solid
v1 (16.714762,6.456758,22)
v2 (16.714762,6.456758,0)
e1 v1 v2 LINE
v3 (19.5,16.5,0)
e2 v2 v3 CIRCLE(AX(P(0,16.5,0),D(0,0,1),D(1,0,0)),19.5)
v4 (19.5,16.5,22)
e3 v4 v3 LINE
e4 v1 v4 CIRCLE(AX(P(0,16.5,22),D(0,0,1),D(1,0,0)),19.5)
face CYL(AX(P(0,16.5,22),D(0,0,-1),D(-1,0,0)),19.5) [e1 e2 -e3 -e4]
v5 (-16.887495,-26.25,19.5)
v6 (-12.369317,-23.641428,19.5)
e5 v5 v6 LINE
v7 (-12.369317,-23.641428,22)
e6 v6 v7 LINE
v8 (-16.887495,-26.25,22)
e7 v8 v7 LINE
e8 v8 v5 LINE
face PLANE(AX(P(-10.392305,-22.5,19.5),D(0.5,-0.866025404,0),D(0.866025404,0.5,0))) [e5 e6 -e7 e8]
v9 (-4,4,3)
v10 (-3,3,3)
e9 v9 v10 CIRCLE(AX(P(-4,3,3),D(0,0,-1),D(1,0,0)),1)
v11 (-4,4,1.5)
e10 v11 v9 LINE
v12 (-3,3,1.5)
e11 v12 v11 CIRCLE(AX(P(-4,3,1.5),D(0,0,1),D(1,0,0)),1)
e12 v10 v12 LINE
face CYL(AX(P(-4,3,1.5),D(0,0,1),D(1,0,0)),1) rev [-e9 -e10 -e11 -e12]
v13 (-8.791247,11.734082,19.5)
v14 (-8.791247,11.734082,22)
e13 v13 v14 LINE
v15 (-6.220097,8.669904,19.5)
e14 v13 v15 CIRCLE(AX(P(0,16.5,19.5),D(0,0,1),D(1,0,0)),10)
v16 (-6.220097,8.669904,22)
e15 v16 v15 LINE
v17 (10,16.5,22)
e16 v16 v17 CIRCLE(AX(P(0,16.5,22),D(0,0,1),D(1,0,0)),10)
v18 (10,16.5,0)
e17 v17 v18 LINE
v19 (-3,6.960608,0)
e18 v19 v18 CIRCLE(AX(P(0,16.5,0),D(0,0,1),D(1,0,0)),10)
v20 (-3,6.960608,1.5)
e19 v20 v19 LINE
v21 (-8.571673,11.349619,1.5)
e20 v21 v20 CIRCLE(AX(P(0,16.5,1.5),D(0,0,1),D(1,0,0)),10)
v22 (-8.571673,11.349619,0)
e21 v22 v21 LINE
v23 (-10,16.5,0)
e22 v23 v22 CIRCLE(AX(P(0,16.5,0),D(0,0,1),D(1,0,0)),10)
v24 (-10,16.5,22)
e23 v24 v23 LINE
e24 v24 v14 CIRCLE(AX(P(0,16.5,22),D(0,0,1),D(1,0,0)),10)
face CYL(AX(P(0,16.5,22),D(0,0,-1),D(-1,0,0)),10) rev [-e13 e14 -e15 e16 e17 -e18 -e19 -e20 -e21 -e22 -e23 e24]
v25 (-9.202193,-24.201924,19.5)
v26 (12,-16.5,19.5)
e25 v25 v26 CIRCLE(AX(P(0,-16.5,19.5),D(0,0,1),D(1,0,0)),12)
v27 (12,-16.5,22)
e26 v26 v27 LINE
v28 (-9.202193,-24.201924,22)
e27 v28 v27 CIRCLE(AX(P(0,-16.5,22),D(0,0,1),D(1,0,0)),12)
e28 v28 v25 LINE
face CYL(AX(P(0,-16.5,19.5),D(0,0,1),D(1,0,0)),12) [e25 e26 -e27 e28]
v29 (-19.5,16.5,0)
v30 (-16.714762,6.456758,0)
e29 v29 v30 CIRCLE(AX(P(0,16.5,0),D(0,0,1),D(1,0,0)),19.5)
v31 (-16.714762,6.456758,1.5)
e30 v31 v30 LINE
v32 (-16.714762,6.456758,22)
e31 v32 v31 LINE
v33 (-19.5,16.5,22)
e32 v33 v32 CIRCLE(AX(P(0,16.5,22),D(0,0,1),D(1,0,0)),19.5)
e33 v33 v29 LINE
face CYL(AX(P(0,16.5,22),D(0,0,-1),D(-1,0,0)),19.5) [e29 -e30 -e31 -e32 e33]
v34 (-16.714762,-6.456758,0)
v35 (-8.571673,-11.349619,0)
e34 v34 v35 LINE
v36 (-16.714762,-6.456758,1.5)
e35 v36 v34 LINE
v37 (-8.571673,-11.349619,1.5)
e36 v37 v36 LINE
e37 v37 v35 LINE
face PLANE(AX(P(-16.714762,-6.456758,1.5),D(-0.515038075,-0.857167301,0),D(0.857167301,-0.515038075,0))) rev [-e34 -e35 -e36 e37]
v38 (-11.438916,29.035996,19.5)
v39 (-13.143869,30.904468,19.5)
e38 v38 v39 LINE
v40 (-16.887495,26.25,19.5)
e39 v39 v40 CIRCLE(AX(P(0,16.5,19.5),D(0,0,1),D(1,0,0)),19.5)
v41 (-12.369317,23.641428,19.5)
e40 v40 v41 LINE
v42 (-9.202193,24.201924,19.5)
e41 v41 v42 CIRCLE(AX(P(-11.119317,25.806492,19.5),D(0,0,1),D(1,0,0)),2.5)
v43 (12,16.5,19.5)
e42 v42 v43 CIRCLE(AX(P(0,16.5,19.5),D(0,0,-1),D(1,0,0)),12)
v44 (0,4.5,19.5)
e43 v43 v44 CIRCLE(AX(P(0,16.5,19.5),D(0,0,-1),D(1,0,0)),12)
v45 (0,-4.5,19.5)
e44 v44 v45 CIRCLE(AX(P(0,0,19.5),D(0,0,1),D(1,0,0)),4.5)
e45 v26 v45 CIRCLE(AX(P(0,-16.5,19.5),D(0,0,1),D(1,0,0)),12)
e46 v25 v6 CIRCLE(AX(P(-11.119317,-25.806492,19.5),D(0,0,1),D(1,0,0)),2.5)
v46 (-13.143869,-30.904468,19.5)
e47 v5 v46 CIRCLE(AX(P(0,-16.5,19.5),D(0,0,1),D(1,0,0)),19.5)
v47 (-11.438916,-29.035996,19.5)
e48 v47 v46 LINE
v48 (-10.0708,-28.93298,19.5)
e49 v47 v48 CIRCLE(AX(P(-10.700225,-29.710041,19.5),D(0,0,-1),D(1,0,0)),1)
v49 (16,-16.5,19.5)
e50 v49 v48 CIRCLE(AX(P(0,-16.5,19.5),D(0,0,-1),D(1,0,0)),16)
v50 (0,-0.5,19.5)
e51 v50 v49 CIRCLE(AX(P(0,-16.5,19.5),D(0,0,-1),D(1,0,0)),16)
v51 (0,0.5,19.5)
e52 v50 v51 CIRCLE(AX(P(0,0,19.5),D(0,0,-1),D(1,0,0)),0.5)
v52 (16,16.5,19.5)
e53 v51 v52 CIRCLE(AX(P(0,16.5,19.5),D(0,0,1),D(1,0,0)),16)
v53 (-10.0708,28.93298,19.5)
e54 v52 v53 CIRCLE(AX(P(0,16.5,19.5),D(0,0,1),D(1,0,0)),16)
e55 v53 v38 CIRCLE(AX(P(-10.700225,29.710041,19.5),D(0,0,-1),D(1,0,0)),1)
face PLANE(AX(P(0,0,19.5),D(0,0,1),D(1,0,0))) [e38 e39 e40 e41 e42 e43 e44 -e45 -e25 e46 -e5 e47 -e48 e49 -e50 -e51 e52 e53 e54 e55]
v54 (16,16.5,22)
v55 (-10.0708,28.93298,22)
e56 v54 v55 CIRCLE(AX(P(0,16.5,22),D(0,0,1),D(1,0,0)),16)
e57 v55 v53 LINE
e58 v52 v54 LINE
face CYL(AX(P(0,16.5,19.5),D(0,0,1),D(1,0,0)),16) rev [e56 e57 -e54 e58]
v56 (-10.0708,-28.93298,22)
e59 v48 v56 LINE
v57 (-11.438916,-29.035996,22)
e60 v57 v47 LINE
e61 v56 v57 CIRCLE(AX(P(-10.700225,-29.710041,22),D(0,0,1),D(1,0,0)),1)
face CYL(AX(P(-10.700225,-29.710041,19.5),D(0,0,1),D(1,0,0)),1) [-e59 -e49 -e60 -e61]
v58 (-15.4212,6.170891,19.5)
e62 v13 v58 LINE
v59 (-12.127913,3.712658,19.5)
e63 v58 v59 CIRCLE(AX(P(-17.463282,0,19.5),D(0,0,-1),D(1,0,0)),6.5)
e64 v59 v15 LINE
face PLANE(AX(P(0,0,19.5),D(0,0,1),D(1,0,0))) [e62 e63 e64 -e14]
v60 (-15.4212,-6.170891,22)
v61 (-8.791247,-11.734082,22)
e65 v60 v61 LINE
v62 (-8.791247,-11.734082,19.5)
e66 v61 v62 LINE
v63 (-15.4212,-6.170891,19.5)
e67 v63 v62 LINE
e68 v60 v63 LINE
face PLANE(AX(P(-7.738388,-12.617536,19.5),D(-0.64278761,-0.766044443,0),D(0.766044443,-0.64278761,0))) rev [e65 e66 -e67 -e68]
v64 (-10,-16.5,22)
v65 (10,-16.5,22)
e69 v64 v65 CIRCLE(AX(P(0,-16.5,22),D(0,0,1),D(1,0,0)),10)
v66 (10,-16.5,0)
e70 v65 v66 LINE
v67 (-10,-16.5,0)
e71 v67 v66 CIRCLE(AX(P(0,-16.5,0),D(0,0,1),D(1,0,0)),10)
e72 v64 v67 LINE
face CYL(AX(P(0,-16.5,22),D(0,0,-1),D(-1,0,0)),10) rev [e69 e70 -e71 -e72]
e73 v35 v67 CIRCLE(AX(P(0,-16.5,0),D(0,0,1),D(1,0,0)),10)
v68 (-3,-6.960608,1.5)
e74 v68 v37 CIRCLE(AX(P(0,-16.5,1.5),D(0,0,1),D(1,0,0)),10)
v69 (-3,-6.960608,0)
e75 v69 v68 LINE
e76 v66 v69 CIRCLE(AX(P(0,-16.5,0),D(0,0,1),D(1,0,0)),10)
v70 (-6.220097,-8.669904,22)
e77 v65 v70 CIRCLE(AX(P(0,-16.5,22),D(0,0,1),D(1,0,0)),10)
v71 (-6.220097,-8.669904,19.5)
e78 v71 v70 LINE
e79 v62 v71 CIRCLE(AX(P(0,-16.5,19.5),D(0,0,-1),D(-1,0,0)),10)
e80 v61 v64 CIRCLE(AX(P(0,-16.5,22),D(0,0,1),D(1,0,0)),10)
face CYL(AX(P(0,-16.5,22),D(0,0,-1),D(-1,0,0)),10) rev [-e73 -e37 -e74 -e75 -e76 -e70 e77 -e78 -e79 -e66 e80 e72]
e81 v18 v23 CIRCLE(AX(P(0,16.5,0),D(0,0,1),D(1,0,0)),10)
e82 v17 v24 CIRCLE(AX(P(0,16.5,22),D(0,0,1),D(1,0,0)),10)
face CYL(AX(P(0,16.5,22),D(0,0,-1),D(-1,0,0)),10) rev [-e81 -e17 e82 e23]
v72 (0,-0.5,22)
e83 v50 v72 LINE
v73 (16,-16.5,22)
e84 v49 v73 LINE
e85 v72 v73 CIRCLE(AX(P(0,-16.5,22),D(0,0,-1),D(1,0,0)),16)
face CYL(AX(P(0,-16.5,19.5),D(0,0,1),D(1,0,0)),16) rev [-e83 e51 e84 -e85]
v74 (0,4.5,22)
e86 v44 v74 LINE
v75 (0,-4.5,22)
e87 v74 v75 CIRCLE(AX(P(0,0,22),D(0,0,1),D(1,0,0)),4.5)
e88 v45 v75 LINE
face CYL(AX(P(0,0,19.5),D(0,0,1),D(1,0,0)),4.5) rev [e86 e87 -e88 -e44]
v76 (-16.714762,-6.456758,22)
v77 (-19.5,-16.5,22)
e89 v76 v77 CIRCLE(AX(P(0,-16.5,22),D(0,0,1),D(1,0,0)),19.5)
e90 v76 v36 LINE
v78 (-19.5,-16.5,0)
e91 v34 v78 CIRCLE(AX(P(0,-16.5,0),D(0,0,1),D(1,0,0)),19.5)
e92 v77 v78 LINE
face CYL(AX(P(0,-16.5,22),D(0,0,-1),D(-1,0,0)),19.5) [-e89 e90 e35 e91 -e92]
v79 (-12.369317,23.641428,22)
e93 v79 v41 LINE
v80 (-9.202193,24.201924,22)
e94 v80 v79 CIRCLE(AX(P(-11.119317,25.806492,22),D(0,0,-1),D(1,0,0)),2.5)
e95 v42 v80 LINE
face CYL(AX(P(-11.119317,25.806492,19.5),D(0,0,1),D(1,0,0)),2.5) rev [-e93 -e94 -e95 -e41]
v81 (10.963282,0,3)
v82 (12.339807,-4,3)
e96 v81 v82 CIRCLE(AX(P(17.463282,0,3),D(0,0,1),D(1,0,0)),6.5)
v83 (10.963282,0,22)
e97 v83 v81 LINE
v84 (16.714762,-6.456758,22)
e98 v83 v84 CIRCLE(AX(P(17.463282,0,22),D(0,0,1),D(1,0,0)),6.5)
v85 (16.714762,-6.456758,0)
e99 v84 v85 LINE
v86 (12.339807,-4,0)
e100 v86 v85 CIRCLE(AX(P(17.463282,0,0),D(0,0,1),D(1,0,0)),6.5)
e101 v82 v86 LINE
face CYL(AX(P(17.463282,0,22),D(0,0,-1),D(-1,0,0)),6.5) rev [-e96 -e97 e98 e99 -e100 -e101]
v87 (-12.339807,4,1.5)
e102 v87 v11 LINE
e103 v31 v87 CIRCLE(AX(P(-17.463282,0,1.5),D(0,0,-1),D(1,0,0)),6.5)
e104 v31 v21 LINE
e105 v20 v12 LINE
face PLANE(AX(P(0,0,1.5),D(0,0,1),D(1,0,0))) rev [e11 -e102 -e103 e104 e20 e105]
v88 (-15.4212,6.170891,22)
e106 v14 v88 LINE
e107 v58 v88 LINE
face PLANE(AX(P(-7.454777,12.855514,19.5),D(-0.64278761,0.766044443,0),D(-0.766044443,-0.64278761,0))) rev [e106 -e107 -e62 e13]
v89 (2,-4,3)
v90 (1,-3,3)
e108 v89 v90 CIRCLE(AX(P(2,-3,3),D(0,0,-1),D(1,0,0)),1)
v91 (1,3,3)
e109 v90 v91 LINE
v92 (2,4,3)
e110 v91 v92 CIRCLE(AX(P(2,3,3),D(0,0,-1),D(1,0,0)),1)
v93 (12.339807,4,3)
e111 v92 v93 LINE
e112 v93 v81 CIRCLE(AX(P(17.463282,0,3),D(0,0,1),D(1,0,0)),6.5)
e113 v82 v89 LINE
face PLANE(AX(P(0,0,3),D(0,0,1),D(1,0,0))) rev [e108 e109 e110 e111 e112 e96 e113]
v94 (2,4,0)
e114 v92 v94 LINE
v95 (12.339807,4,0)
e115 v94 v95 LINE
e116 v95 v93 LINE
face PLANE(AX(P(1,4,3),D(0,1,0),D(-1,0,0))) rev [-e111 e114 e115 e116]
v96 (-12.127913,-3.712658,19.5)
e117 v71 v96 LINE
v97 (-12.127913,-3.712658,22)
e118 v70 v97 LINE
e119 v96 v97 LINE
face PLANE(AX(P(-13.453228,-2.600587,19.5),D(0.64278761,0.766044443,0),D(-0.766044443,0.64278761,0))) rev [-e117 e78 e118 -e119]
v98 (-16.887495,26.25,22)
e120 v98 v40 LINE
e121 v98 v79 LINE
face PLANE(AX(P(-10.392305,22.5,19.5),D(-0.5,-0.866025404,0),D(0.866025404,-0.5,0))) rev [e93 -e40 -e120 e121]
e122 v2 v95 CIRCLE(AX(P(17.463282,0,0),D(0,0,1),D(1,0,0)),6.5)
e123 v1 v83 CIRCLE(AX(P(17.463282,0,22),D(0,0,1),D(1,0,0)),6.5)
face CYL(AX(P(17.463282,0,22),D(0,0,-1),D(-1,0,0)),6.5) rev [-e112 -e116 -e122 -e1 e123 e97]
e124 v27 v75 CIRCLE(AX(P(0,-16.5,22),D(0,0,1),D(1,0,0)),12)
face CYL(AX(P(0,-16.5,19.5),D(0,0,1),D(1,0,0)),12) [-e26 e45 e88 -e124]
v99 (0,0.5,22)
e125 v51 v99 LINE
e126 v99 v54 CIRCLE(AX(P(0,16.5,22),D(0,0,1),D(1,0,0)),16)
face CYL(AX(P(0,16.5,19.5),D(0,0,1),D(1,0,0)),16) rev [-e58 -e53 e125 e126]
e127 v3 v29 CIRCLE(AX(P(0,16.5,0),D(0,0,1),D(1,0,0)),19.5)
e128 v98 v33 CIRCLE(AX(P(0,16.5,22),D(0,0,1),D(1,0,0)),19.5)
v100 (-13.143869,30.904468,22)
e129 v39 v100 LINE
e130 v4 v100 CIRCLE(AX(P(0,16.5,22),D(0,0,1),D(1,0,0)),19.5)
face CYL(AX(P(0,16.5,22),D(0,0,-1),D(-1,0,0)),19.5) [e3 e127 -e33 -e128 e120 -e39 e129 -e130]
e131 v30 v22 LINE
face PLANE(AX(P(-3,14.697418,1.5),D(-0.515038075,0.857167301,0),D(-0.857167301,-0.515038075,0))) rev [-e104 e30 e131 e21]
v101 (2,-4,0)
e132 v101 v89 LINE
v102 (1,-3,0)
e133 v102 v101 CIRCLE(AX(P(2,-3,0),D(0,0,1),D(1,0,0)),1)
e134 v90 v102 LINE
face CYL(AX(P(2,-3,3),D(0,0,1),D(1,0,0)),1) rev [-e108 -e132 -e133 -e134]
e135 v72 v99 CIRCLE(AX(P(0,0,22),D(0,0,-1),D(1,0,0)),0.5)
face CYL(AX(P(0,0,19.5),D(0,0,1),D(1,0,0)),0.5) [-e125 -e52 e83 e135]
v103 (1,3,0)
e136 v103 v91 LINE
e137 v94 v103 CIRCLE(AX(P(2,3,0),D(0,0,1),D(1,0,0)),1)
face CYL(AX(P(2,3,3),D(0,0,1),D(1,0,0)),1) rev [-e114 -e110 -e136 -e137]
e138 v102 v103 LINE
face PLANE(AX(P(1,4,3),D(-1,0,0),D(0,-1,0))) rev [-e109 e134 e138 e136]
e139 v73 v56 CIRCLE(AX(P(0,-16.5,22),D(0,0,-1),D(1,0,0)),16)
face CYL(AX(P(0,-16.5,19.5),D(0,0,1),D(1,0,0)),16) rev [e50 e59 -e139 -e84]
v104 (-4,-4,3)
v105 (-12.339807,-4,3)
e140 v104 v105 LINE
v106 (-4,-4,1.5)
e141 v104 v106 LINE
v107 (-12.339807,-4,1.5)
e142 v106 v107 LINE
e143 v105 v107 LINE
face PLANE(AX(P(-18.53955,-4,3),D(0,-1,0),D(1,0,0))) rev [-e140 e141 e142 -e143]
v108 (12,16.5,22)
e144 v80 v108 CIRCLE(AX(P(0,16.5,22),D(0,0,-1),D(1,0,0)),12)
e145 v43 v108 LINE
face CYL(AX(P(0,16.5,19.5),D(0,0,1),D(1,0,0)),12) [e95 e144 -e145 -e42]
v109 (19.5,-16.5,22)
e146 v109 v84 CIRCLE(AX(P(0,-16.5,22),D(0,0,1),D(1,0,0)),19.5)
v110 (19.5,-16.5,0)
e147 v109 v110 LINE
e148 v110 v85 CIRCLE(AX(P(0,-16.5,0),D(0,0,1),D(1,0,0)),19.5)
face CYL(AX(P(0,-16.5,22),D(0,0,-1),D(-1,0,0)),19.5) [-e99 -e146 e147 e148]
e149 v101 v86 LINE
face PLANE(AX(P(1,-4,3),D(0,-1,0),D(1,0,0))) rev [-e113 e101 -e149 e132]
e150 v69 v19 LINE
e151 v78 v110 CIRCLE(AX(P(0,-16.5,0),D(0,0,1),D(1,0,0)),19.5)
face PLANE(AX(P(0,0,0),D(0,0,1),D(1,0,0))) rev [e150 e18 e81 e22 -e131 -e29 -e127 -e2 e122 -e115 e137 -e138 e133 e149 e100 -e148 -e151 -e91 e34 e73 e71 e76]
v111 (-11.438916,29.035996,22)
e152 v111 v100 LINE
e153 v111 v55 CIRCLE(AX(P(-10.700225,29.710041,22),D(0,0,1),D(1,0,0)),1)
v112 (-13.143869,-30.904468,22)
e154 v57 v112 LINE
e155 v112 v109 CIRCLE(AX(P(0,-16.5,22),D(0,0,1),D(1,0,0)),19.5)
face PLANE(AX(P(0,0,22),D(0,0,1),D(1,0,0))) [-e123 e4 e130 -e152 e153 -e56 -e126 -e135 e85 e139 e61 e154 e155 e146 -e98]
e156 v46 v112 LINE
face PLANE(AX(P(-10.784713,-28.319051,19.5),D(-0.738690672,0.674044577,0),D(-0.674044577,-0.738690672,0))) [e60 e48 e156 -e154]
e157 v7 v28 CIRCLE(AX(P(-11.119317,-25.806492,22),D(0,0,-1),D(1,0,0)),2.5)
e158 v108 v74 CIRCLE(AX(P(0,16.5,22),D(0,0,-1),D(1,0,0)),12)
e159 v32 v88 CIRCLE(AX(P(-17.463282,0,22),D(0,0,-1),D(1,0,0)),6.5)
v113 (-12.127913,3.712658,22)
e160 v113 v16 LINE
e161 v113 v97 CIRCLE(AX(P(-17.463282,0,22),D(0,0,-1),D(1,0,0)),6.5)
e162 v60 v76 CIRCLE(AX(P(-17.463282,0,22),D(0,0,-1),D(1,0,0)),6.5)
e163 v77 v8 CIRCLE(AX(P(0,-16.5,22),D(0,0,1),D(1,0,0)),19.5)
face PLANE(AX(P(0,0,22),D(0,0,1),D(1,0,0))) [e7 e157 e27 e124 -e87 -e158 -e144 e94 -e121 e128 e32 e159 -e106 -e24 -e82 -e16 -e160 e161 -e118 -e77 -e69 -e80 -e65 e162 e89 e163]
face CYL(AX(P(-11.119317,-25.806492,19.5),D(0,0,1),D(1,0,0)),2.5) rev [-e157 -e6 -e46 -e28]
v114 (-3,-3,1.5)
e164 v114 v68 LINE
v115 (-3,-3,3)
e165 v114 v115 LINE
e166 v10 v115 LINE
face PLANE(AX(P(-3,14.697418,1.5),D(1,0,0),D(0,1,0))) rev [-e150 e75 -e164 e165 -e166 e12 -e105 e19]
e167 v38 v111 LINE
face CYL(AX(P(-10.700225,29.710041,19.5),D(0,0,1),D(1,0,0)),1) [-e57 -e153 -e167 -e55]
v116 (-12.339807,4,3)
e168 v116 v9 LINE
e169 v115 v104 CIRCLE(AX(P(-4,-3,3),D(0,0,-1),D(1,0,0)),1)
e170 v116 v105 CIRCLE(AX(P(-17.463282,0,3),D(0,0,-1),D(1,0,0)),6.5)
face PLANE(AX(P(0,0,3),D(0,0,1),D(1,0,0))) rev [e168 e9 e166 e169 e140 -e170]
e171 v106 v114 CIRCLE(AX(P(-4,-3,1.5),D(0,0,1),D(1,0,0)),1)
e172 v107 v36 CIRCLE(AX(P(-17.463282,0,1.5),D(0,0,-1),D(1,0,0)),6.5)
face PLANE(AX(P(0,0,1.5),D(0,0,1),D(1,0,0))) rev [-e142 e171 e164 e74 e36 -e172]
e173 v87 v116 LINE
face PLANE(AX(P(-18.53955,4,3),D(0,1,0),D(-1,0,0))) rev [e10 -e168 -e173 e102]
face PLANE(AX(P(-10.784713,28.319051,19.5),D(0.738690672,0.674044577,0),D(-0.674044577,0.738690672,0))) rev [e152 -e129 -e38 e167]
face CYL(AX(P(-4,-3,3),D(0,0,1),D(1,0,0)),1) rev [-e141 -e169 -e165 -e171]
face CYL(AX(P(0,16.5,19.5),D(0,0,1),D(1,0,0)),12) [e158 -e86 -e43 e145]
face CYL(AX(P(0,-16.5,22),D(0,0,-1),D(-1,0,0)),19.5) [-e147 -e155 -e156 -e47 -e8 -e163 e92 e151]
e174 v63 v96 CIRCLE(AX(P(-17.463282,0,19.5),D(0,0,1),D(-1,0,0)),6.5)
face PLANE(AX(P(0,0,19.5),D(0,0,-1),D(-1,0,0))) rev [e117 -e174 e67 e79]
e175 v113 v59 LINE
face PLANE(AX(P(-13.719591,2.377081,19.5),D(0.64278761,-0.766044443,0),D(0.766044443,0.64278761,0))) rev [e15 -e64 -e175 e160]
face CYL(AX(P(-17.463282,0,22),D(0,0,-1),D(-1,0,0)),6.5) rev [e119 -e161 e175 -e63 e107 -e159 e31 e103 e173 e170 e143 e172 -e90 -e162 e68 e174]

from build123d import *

# Parameters (mm, degrees)
SKETCH_1_R             = 10
EXTRUDE_1_DEPTH        = 22
CUT_EXTRUDE_1_DEPTH    = 2.5
FILLET_1_R             = 1
FILLET_2_R             = 2.5
FILLET_1_OF_MIRROR_1_R = 1
FILLET_2_OF_MIRROR_1_R = 2.5
CUT_EXTRUDE_2_DEPTH    = 2.5
CUT_EXTRUDE_3_DEPTH    = 1.5
SKETCH_5_W             = 15.539550215
SKETCH_5_H             = 8
CUT_EXTRUDE_4_DEPTH    = 1.5
SKETCH_6_W             = 13.998675607
SKETCH_6_H             = 8
CUT_EXTRUDE_5_DEPTH    = 3
FILLET_3_R             = 1


with BuildPart() as part:
    # 草图1 → 凸台-拉伸1 (new body)
    with BuildSketch(Plane.XY):
        with BuildLine():
            ThreePointArc((16.714762364, 6.456757539), (0, 36), (-16.714762364, 6.456757539))
            ThreePointArc((-16.714762364, 6.456757539), (-10.963282289, 0), (-16.714762364, -6.456757539))
            ThreePointArc((-16.714762364, -6.456757539), (0, -36), (16.714762364, -6.456757539))
            ThreePointArc((16.714762364, -6.456757539), (10.963282289, 0), (16.714762364, 6.456757539))
        make_face()
        with Locations((0, 16.5)):
            Circle(SKETCH_1_R, mode=Mode.SUBTRACT)
        with Locations((0, -16.5)):
            Circle(SKETCH_1_R, mode=Mode.SUBTRACT)
    extrude(amount=EXTRUDE_1_DEPTH)

    # 草图2 → 切除-拉伸1 (cut)
    with BuildSketch(Plane.XY.offset(22)):
        with BuildLine():
            Line((-10.392304845, 22.5), (-20.279992845, 28.208659328))
            Line((-20.279992845, 28.208659328), (-16.120486586, 34.166566083))
            Line((-16.120486586, 34.166566083), (-10.784713231, 28.319050745))
            ThreePointArc((-10.784713231, 28.319050745), (14.918190439, 22.283389494), (0, 0.5))
            ThreePointArc((0, 0.5), (-0.353553391, 0.353553391), (-0.5, 0))
            Line((-0.5, 0), (-4.5, 0))
            ThreePointArc((-4.5, 0), (-3.181980515, 3.181980515), (0, 4.5))
            ThreePointArc((0, 4.5), (10.392304845, 22.5), (-10.392304845, 22.5))
        make_face()
    cut_extrude_1 = extrude(amount=-CUT_EXTRUDE_1_DEPTH, mode=Mode.SUBTRACT)

    # 圆角1
    fillet_1_edges = [part.edges().sort_by_distance(p)[0] for p in [
        (-10.784713231, 28.319050745, 20.75),
    ]]
    fillet(fillet_1_edges, radius=FILLET_1_R)

    # 圆角2
    fillet_2_edges = [part.edges().sort_by_distance(p)[0] for p in [
        (-10.392304845, 22.5, 20.75),
    ]]
    fillet(fillet_2_edges, radius=FILLET_2_R)

    # 镜向1: 切除-拉伸1 across plane
    add(cut_extrude_1.mirror(Plane.ZX), mode=Mode.SUBTRACT)

    # 圆角1 of 镜向1
    fillet_1_of_mirror_1_edges = [part.edges().sort_by_distance(p)[0] for p in [
        (-10.784713231, -28.319050745, 20.75),
    ]]
    fillet(fillet_1_of_mirror_1_edges, radius=FILLET_1_OF_MIRROR_1_R)

    # 圆角2 of 镜向1
    fillet_2_of_mirror_1_edges = [part.edges().sort_by_distance(p)[0] for p in [
        (-10.392304845, -22.5, 20.75),
    ]]
    fillet(fillet_2_of_mirror_1_edges, radius=FILLET_2_OF_MIRROR_1_R)

    # 草图3 → 切除-拉伸2 (cut)
    with BuildSketch(Plane.XY.offset(22)):
        Polygon((-7.454777322, 12.855513677), (-16.290741775, 5.441259163), (-13.719591337, 2.377081391), (-4.883626883, 9.791335905), align=None)
        Polygon((-13.453227562, -2.600587136), (-5.167237951, -9.553357963), (-7.738388389, -12.617535735), (-16.448259291, -5.309086274), align=None)
    extrude(amount=-CUT_EXTRUDE_2_DEPTH, mode=Mode.SUBTRACT)

    # 草图4 → 切除-拉伸3 (cut)
    with BuildSketch(Plane(origin=(0, 0, 0), x_dir=(-1, 0, 0), z_dir=(0, 0, -1))):
        Polygon((3, 14.697418143), (16.714762364, 6.456757539), (16.714762364, -6.456757539), (3, -14.697418143), align=None)
    extrude(amount=-CUT_EXTRUDE_3_DEPTH, mode=Mode.SUBTRACT)

    # 草图5 → 切除-拉伸4 (cut)
    with BuildSketch(Plane(origin=(0, 0, 1.5), x_dir=(-1, 0, 0), z_dir=(0, 0, -1))):
        with Locations((10.769775108, 0)):
            Rectangle(SKETCH_5_W, SKETCH_5_H)
    extrude(amount=-CUT_EXTRUDE_4_DEPTH, mode=Mode.SUBTRACT)

    # 草图6 → 切除-拉伸5 (cut)
    with BuildSketch(Plane(origin=(0, 0, 0), x_dir=(-1, 0, 0), z_dir=(0, 0, -1))):
        with Locations((-7.999337804, 0)):
            Rectangle(SKETCH_6_W, SKETCH_6_H)
    extrude(amount=-CUT_EXTRUDE_5_DEPTH, mode=Mode.SUBTRACT)

    # 圆角3
    fillet_3_edges = [part.edges().sort_by_distance(p)[0] for p in [
        (-3, 4, 2.25),
        (-3, -4, 2.25),
        (1, 4, 1.5),
        (1, -4, 1.5),
    ]]
    fillet(fillet_3_edges, radius=FILLET_3_R)


solid = part.part
